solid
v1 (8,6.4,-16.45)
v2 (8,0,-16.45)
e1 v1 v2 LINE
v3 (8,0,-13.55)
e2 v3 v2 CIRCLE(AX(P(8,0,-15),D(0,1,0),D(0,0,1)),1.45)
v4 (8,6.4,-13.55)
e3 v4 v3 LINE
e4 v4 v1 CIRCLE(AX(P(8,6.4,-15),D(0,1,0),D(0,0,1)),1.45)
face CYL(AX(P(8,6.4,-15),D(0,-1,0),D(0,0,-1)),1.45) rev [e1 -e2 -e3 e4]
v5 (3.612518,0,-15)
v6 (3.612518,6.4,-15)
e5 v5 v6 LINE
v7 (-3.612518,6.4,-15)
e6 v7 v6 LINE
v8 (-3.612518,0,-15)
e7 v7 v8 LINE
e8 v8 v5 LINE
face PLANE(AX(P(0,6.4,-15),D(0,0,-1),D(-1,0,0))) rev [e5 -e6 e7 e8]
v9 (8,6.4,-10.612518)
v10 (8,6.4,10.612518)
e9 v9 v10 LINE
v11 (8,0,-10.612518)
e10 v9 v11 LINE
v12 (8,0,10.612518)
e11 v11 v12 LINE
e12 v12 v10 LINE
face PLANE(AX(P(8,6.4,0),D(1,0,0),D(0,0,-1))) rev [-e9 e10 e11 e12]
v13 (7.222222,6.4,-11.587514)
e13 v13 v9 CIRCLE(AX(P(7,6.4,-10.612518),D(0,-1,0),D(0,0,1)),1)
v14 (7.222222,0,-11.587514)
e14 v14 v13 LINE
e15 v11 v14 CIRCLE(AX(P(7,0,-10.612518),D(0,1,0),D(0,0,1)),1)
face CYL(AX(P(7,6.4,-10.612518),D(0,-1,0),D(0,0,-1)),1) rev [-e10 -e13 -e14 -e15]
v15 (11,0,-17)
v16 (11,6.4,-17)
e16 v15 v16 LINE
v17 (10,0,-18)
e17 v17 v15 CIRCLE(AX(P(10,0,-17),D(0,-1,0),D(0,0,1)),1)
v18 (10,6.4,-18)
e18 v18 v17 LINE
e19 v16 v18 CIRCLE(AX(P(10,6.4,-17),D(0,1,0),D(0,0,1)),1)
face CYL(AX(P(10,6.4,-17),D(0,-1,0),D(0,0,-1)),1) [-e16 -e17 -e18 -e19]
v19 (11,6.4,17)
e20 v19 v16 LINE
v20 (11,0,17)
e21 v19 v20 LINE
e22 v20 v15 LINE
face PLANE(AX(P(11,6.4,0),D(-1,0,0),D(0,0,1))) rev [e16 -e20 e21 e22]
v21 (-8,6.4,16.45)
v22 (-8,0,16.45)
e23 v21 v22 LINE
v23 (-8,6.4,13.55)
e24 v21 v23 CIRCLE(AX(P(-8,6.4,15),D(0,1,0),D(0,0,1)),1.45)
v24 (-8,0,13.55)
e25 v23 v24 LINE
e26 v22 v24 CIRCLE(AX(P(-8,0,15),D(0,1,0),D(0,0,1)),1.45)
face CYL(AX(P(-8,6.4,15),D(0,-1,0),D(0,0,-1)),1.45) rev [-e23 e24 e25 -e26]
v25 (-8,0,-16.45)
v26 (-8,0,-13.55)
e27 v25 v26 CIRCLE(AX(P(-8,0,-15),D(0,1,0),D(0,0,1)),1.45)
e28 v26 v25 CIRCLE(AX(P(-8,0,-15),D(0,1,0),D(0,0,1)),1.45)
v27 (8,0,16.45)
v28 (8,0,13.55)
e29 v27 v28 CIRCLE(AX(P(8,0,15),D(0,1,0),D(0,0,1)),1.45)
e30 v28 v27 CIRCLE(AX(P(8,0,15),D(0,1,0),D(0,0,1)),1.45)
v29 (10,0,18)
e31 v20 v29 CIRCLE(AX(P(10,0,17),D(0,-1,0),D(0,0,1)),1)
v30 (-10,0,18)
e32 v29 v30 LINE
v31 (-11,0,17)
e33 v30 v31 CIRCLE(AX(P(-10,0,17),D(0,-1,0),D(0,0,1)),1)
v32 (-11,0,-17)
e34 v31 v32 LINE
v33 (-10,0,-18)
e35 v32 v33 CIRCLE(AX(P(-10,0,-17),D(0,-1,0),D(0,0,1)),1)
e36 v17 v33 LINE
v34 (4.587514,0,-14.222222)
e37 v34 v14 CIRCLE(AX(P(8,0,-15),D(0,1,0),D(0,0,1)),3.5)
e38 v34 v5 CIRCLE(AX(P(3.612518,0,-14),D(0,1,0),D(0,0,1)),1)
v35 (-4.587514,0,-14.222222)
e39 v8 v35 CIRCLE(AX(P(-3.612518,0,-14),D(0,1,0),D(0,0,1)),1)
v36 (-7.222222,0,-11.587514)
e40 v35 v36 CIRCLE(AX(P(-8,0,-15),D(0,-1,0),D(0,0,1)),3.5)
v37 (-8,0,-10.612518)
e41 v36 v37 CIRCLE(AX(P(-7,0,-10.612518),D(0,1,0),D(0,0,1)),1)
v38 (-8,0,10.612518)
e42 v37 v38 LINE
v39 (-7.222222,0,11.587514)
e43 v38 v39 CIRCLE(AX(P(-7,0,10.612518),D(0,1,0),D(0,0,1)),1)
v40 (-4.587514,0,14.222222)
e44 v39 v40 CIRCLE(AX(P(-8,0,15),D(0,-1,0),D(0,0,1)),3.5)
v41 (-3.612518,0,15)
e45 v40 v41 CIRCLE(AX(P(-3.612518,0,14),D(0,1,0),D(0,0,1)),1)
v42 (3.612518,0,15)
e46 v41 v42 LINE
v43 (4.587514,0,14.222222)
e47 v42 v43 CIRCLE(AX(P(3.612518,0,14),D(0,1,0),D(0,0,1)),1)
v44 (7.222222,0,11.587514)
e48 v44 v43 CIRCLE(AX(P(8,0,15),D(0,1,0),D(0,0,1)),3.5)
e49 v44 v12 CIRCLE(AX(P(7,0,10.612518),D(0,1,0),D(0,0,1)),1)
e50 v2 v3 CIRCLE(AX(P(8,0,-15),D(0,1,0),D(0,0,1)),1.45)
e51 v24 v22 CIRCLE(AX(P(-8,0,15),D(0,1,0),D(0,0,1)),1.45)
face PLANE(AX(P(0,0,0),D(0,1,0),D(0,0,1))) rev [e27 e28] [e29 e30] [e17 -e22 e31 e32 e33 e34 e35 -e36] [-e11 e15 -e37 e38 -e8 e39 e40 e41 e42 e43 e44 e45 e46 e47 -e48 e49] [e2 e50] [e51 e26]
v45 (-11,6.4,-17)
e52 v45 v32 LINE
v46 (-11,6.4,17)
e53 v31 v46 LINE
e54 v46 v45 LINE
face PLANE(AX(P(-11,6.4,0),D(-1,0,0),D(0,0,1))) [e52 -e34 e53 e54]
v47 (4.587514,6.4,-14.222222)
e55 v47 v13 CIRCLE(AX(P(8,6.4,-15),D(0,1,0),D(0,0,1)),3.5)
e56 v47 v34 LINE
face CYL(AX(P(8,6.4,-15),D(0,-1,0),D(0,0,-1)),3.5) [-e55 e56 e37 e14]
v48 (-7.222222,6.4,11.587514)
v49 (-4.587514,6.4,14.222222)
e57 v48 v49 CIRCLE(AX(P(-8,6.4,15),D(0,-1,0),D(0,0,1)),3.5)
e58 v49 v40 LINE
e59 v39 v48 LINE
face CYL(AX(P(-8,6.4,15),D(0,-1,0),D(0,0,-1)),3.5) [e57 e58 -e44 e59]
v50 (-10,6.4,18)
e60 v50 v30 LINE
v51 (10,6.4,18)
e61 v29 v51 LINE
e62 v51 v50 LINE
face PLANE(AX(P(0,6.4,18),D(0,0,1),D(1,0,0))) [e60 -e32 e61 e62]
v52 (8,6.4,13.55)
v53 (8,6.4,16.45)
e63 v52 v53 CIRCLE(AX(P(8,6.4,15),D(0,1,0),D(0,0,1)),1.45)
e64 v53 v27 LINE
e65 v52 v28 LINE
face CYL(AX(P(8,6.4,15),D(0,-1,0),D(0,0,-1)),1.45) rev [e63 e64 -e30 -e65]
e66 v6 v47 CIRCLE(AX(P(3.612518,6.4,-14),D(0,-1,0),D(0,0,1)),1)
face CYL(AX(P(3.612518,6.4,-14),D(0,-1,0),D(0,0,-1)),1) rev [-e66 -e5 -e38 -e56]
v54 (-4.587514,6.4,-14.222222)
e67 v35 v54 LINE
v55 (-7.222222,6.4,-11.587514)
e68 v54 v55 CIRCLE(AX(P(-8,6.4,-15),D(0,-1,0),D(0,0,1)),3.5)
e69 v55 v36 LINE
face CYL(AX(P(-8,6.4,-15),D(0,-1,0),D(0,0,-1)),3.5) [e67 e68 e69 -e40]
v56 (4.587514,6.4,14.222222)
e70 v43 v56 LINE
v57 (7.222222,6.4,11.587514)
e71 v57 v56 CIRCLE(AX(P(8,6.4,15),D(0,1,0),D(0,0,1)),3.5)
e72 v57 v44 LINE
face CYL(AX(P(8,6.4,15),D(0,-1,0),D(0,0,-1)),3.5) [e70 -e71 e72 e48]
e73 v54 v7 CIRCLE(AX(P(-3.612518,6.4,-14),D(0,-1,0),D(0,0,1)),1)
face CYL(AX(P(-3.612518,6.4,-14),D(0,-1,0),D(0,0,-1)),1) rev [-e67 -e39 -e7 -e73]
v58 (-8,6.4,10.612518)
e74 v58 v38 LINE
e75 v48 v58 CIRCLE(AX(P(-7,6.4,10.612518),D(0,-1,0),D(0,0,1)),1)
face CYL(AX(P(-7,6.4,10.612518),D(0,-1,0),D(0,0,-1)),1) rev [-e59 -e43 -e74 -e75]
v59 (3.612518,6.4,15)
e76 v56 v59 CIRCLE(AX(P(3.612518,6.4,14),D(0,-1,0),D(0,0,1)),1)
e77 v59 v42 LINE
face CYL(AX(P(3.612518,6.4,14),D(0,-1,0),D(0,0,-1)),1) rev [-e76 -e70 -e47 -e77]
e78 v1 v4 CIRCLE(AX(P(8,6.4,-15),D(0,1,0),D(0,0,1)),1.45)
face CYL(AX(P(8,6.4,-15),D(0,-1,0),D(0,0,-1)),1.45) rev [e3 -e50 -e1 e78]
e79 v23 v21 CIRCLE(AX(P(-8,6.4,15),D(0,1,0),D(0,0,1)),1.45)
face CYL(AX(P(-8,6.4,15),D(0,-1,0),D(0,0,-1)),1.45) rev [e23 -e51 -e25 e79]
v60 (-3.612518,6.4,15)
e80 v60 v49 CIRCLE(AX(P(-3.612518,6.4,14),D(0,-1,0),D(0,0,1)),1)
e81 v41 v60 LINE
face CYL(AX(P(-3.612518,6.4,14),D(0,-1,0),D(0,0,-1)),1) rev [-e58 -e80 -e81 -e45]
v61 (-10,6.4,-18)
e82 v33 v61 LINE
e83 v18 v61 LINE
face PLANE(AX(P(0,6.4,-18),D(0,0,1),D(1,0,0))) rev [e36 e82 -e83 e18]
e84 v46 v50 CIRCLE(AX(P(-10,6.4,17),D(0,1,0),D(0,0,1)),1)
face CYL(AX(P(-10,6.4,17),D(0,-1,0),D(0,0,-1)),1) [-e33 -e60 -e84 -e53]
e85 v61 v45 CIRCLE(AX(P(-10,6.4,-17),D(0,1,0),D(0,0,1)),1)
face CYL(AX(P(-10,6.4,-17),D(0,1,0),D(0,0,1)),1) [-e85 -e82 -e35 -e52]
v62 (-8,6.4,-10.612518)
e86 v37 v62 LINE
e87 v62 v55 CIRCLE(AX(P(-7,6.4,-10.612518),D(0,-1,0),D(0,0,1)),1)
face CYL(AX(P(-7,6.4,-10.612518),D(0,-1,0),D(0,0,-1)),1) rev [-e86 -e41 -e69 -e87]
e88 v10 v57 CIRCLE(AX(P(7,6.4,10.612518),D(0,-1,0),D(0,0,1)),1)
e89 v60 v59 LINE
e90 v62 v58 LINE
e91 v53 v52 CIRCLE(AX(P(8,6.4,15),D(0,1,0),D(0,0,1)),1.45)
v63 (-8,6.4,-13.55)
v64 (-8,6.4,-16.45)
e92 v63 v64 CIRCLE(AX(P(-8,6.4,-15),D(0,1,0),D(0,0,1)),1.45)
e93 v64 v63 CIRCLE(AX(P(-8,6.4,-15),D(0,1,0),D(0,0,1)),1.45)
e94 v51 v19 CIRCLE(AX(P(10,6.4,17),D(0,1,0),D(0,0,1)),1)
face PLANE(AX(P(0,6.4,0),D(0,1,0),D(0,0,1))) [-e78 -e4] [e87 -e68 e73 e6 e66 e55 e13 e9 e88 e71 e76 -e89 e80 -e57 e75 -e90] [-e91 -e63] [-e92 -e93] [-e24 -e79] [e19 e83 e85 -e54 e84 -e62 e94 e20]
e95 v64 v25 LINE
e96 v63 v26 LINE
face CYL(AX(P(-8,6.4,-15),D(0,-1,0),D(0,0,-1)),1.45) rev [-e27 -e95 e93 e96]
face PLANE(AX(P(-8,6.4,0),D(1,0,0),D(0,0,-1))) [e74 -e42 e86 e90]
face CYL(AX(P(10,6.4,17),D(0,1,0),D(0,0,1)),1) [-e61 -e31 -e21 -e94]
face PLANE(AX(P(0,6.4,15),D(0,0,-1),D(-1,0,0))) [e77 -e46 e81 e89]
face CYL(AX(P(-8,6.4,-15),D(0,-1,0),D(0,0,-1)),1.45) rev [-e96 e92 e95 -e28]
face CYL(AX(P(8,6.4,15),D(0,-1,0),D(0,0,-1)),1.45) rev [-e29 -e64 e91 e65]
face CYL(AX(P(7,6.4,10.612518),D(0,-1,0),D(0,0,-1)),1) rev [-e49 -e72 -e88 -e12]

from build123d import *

# Parameters (mm, degrees)
SKETCH_1_W      = 22
SKETCH_1_H      = 36
SKETCH_1_R      = 1.45
EXTRUDE_1_DEPTH = 6.4
FILLET_1_R      = 1
FILLET_2_R      = 1


with BuildPart() as part:
    # 草图1 → 凸台-拉伸1 (new body)
    with BuildSketch(Plane(origin=(0, 0, 0), x_dir=(1, 0, 0), z_dir=(0, 1, 0))):
        Rectangle(SKETCH_1_W, SKETCH_1_H)
        with Locations(Location((-8, 15, 0), (0, 0, 270))):
            Circle(SKETCH_1_R, mode=Mode.SUBTRACT)
        with Locations(Location((8, 15, 0), (0, 0, 270))):
            Circle(SKETCH_1_R, mode=Mode.SUBTRACT)
        with Locations(Location((-8, -15, 0), (0, 0, 270))):
            Circle(SKETCH_1_R, mode=Mode.SUBTRACT)
        with Locations(Location((8, -15, 0), (0, 0, 270))):
            Circle(SKETCH_1_R, mode=Mode.SUBTRACT)
        with BuildLine():
            Line((-4.5, 15), (4.5, 15))
            ThreePointArc((4.5, 15), (5.525126266, 12.525126266), (8, 11.5))
            Line((8, 11.5), (8, -11.5))
            ThreePointArc((8, -11.5), (5.525126266, -12.525126266), (4.5, -15))
            Line((4.5, -15), (-4.5, -15))
            ThreePointArc((-4.5, -15), (-5.525126266, -12.525126266), (-8, -11.5))
            Line((-8, -11.5), (-8, 11.5))
            ThreePointArc((-8, 11.5), (-5.525126266, 12.525126266), (-4.5, 15))
        make_face(mode=Mode.SUBTRACT)
    extrude(amount=EXTRUDE_1_DEPTH)

    # 圆角1
    fillet_1_edges = [part.edges().sort_by_distance(p)[0] for p in [
        (8, 3.2, -11.5),
        (4.5, 3.2, -15),
        (-4.5, 3.2, -15),
        (-8, 3.2, -11.5),
        (-8, 3.2, 11.5),
        (-4.5, 3.2, 15),
        (4.5, 3.2, 15),
        (8, 3.2, 11.5),
    ]]
    fillet(fillet_1_edges, radius=FILLET_1_R)

    # 圆角2
    fillet_2_edges = [part.edges().sort_by_distance(p)[0] for p in [
        (-11, 3.2, -18),
        (11, 3.2, -18),
        (11, 3.2, 18),
        (-11, 3.2, 18),
    ]]
    fillet(fillet_2_edges, radius=FILLET_2_R)


solid = part.part
